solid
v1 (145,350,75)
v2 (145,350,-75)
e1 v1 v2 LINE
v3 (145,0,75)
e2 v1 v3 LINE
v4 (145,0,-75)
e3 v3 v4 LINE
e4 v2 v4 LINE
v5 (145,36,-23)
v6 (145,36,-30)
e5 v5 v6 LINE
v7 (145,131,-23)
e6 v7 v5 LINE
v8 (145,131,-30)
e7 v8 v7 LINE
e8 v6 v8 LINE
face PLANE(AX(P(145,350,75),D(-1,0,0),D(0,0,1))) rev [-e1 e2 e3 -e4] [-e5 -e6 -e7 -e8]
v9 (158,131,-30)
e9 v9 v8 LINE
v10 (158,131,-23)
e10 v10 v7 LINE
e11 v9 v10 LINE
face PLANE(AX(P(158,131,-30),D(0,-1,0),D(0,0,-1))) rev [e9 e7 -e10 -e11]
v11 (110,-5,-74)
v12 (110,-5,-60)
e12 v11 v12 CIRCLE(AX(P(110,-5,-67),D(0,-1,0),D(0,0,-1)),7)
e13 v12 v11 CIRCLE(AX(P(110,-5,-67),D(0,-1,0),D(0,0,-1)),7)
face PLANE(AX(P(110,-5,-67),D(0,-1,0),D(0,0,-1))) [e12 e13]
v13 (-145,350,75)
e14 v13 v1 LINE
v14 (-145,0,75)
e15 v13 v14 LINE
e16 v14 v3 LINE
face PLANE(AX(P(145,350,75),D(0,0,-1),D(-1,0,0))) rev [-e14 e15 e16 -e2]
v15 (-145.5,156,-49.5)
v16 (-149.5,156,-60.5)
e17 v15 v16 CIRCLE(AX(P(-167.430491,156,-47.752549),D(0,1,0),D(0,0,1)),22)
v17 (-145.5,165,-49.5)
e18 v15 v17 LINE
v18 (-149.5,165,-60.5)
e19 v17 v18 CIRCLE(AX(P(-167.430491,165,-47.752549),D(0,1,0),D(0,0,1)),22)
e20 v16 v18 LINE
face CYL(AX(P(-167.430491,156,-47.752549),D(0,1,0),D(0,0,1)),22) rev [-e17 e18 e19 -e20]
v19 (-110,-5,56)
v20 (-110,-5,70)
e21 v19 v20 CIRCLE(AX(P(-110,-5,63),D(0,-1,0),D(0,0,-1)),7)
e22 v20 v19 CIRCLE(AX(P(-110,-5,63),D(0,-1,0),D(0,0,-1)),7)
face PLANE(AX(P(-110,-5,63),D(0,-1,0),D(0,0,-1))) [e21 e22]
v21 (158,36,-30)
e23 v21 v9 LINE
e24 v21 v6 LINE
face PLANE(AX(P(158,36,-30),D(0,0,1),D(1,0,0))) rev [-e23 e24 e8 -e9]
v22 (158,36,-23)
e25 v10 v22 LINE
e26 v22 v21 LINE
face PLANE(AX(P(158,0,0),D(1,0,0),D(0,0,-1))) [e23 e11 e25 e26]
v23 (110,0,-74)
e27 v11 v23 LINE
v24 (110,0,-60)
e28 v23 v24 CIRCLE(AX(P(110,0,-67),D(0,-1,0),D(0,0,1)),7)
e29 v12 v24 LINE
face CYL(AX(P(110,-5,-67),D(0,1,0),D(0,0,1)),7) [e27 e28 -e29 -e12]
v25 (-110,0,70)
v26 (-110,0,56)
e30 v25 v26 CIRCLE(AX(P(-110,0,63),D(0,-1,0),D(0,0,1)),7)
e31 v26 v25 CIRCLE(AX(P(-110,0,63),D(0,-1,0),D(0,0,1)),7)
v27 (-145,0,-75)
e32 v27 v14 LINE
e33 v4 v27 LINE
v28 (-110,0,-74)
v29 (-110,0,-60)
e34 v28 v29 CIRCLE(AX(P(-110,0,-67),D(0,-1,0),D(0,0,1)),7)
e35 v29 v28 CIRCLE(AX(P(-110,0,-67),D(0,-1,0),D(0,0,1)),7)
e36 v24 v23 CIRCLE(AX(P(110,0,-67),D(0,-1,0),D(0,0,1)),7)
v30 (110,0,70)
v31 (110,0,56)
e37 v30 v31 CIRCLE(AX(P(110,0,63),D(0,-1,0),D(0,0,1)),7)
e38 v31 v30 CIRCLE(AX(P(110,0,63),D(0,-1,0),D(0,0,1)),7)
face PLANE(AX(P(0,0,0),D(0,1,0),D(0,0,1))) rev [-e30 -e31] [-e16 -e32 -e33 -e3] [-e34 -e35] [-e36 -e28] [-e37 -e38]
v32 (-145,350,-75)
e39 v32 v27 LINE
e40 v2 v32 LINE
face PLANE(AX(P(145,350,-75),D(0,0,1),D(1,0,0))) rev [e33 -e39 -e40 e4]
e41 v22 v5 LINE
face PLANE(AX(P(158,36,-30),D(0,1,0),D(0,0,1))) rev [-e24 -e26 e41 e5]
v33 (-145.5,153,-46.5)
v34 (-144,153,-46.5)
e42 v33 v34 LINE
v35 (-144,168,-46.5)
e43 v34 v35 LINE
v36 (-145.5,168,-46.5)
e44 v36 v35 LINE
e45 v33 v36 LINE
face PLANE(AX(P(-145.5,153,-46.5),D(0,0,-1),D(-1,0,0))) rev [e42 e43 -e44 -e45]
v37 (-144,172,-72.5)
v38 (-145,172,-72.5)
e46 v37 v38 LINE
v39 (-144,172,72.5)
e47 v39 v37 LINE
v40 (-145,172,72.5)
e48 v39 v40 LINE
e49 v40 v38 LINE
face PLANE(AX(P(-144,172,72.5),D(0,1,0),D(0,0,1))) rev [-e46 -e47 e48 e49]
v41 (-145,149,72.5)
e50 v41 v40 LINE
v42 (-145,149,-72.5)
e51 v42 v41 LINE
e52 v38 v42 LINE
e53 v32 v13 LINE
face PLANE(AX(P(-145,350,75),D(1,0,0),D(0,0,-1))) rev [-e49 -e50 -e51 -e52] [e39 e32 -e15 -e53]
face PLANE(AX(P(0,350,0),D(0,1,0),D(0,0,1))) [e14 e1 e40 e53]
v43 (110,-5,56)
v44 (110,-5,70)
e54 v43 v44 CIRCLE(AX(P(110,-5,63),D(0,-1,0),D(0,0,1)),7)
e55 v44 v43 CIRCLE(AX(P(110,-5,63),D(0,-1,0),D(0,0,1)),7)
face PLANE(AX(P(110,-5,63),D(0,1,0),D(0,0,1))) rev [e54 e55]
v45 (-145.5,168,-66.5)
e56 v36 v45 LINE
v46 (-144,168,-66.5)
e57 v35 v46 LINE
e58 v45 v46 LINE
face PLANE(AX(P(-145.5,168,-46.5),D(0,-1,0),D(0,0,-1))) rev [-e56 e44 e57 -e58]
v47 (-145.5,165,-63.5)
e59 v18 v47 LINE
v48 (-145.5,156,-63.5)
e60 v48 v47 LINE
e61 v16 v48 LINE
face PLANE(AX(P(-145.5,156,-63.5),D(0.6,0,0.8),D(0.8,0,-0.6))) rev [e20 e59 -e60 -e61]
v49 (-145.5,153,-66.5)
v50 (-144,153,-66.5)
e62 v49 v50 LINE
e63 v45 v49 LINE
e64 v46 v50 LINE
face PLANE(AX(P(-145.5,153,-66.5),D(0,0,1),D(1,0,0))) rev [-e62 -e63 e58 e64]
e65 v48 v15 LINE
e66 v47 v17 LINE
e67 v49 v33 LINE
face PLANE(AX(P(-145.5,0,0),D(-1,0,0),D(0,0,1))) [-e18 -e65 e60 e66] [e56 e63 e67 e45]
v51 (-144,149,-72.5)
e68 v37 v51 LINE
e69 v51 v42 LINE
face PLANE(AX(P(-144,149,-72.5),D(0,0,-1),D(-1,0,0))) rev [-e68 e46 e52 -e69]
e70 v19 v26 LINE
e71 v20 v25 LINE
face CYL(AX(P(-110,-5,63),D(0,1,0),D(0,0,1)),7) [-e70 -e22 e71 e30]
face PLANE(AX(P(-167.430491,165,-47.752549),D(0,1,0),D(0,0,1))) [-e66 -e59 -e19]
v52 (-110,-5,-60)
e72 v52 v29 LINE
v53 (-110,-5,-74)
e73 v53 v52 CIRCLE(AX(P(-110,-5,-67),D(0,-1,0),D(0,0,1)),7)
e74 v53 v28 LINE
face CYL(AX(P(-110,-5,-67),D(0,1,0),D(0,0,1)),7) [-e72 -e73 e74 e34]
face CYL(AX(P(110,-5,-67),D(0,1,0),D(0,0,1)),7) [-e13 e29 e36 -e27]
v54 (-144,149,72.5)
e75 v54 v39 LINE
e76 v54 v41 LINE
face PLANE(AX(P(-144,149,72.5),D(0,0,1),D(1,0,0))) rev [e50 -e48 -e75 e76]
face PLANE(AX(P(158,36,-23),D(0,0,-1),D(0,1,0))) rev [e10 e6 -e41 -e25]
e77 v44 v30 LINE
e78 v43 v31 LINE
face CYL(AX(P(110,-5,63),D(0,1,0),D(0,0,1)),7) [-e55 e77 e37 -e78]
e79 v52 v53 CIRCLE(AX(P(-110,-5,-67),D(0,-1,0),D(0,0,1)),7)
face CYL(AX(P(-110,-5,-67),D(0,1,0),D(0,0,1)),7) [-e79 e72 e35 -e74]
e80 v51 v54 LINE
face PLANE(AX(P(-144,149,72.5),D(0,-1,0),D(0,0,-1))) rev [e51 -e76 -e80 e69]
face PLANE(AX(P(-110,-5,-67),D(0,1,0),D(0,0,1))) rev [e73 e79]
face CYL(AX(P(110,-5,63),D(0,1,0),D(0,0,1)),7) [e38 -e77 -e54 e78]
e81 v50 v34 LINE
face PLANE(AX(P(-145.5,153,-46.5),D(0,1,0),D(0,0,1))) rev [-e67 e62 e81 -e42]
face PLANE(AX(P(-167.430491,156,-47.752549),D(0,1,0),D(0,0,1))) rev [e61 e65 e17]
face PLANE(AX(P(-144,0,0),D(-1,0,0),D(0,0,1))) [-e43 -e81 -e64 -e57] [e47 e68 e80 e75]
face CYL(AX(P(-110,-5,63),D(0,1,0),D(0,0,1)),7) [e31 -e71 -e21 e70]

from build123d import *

# Parameters (mm, degrees)
SKETCH_1_W          = 290
SKETCH_1_H          = 150
EXTRUDE_1_DEPTH     = 350
SKETCH_2_R          = 7
EXTRUDE_2_DEPTH     = 5
SKETCH_3_W          = 145
SKETCH_3_H          = 23
CUT_EXTRUDE_1_DEPTH = 1
SKETCH_4_W          = 20
SKETCH_4_H          = 15
EXTRUDE_3_DEPTH     = 1.5
EXTRUDE_4_DEPTH     = 4.5
SKETCH_6_W          = 7
SKETCH_6_H          = 95
EXTRUDE_5_DEPTH     = 13


with BuildPart() as part:
    # 草图1 → 凸台-拉伸1 (new body)
    with BuildSketch(Plane(origin=(0, 0, 0), x_dir=(1, 0, 0), z_dir=(0, 1, 0))):
        Rectangle(SKETCH_1_W, SKETCH_1_H)
    extrude(amount=EXTRUDE_1_DEPTH)

    # 草图2 → 凸台-拉伸2 (add)
    with BuildSketch(Plane.XZ):
        with Locations(Location((-110, 63, 0), (0, 0, 90))):
            Circle(SKETCH_2_R)
        with Locations(Location((110, 63, 0), (0, 0, 90))):
            Circle(SKETCH_2_R)
        with Locations(Location((110, -67, 0), (0, 0, 90))):
            Circle(SKETCH_2_R)
        with Locations(Location((-110, -67, 0), (0, 0, 90))):
            Circle(SKETCH_2_R)
    extrude(amount=EXTRUDE_2_DEPTH)

    # 草图3 → 切除-拉伸1 (cut)
    with BuildSketch(Plane.ZY.offset(145)):
        with Locations((0, 160.5)):
            Rectangle(SKETCH_3_W, SKETCH_3_H)
    extrude(amount=-CUT_EXTRUDE_1_DEPTH, mode=Mode.SUBTRACT)

    # 草图4 → 凸台-拉伸3 (add)
    with BuildSketch(Plane.ZY.offset(144)):
        with Locations((-56.5, 160.5)):
            Rectangle(SKETCH_4_W, SKETCH_4_H)
    extrude(amount=EXTRUDE_3_DEPTH)

    # 草图5 → 凸台-拉伸4 (add, symmetric)
    with BuildSketch(Plane(origin=(0, 160.5, 0), x_dir=(-1, 0, 0), z_dir=(0, -1, 0))):
        with BuildLine():
            Line((145.5, 63.5), (149.5, 60.5))
            ThreePointArc((149.5, 60.5), (146.755035208, 55.270896288), (145.5, 49.5))
            Line((145.5, 49.5), (145.5, 63.5))
        make_face()
    extrude(amount=EXTRUDE_4_DEPTH, both=True)

    # 草图6 → 凸台-拉伸5 (add)
    with BuildSketch(Plane(origin=(145, 0, 0), x_dir=(0, 0, -1), z_dir=(1, 0, 0))):
        with Locations((26.5, 83.5)):
            Rectangle(SKETCH_6_W, SKETCH_6_H)
    extrude(amount=EXTRUDE_5_DEPTH)


solid = part.part
